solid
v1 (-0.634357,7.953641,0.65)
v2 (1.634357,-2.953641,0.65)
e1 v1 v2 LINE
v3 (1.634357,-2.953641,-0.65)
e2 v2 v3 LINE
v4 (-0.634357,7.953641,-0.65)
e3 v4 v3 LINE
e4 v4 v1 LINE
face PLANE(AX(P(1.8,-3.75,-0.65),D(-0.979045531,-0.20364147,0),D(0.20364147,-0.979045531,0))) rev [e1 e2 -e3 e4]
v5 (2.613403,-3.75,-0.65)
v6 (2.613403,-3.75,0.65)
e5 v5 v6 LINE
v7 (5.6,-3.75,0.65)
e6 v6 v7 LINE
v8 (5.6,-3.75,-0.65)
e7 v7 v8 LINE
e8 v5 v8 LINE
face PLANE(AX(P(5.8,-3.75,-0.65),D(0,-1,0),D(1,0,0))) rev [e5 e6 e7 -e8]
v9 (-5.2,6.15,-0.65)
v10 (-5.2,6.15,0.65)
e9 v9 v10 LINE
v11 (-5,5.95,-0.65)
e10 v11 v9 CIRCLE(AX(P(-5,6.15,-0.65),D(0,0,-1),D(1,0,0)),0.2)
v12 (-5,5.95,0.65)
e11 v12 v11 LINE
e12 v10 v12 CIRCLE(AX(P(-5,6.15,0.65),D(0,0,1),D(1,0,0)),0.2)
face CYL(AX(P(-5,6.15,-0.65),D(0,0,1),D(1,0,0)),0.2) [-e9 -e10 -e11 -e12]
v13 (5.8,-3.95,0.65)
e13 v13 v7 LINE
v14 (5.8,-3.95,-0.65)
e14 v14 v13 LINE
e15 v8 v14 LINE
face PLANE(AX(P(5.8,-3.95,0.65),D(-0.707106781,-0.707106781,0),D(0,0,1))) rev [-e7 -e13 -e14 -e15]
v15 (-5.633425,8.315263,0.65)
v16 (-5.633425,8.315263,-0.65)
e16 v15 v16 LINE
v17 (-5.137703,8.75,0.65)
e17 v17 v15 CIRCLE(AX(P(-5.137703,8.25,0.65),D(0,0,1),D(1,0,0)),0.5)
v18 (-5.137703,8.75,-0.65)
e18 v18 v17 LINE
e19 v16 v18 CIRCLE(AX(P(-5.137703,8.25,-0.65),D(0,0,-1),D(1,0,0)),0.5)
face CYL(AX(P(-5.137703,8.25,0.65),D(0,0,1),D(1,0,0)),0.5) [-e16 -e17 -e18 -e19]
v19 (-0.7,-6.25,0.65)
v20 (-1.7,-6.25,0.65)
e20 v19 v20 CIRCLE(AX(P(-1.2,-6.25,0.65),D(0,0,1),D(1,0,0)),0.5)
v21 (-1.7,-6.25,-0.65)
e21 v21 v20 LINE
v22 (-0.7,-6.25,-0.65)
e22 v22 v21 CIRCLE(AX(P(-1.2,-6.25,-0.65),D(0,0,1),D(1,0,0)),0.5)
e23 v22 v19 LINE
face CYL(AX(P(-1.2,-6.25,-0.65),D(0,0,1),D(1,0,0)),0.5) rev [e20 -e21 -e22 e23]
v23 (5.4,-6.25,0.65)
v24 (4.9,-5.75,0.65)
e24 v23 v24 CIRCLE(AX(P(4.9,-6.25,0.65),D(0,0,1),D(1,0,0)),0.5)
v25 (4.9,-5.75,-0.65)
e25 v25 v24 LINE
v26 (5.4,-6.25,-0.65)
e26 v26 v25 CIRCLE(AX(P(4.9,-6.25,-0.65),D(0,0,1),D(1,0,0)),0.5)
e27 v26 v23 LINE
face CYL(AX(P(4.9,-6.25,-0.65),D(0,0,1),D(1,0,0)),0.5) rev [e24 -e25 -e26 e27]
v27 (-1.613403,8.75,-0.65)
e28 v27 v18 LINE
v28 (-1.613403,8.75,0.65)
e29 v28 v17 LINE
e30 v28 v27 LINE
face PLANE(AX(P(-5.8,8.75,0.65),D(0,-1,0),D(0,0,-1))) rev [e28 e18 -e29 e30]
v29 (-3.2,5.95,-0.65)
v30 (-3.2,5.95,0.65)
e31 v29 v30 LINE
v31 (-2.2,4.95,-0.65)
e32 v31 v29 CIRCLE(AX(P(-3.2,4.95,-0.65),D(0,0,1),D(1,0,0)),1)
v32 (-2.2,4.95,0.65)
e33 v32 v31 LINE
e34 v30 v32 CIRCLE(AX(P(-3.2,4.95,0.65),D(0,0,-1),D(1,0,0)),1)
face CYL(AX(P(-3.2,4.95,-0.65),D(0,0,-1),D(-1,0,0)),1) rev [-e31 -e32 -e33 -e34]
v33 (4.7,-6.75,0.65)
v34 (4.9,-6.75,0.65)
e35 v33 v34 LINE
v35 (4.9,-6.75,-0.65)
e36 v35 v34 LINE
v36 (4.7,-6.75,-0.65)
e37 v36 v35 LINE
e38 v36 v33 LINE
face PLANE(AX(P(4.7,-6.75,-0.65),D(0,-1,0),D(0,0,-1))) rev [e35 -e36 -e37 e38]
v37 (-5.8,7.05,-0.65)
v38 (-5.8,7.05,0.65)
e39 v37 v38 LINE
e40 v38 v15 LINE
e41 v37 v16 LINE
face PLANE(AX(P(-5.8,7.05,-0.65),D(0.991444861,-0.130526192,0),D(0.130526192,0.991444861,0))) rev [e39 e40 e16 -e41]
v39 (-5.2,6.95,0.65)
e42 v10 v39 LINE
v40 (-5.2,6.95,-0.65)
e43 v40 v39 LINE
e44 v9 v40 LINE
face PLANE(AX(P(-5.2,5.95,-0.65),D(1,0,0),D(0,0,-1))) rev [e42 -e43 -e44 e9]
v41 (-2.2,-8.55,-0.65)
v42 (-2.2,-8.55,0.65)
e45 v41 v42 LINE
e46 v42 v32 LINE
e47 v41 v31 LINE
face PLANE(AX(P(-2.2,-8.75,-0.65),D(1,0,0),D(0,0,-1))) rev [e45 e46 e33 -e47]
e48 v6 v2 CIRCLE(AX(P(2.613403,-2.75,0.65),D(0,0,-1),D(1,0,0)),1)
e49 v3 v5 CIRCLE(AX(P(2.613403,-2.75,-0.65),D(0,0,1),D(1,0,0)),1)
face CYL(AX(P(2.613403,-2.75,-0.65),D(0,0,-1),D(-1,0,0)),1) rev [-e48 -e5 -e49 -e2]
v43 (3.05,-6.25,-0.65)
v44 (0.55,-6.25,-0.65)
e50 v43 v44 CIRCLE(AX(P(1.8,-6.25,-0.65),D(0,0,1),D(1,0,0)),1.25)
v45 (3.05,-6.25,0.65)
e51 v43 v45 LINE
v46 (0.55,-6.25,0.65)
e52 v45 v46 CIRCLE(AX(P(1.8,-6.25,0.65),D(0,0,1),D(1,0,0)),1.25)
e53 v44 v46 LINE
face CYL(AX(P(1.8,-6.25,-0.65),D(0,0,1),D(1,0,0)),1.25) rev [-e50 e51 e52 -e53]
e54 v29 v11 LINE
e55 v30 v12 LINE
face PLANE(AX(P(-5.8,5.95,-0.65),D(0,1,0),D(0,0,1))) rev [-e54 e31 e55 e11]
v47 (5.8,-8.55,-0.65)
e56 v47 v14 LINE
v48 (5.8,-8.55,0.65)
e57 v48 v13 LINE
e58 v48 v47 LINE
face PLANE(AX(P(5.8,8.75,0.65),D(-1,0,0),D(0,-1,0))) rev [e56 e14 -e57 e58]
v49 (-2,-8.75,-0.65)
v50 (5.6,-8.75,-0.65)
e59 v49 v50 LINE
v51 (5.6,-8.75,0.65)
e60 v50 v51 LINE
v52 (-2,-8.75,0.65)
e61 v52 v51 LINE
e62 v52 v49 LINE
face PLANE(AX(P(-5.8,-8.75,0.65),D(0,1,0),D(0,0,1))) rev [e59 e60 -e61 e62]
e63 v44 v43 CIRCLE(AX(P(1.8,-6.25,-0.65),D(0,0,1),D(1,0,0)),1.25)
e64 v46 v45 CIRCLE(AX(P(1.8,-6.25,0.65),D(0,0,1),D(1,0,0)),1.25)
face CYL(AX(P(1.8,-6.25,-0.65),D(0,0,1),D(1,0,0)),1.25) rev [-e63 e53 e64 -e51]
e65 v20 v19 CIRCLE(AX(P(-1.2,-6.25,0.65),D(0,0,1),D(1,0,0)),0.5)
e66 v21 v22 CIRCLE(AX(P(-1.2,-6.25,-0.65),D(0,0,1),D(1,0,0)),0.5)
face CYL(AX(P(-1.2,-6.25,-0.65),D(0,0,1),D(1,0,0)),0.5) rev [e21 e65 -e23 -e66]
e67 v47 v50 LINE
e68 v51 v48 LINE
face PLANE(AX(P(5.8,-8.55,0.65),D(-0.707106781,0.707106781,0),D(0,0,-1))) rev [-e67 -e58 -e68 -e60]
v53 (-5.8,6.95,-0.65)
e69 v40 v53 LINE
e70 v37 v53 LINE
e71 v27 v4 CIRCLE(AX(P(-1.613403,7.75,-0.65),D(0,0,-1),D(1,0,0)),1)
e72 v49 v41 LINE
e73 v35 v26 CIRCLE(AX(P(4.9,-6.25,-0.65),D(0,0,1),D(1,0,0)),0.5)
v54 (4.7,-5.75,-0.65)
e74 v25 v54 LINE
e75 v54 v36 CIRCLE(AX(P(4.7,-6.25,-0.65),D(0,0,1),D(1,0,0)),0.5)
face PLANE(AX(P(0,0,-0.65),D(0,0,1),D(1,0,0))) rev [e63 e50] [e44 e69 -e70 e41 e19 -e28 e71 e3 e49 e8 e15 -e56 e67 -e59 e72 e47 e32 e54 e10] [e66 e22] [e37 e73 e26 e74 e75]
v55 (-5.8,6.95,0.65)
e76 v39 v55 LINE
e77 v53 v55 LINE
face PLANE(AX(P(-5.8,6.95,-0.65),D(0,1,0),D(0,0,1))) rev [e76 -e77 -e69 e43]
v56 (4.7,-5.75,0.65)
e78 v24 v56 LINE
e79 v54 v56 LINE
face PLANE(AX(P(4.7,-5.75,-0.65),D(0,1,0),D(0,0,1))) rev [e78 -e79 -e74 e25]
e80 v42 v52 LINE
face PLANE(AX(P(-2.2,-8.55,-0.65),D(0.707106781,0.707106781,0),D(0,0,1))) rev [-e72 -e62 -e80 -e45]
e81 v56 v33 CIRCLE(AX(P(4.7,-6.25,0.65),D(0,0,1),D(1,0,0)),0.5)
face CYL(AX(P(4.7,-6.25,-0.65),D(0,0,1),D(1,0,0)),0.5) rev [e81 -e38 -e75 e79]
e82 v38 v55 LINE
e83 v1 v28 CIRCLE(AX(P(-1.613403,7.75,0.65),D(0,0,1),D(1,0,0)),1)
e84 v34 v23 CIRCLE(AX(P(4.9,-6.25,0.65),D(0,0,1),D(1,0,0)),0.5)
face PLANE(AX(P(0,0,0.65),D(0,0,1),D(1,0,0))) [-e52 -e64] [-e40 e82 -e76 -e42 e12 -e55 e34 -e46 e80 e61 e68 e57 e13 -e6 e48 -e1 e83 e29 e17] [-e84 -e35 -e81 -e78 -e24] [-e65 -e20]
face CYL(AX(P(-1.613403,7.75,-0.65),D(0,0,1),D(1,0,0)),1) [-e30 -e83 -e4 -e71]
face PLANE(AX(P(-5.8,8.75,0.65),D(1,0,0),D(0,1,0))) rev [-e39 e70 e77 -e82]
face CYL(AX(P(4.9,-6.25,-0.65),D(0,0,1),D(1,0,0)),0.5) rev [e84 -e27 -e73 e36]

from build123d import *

# Parameters (mm, degrees)
SKETCH1_W           = 11.6
SKETCH1_H           = 17.5
BOSS_EXTRUDE1_DEPTH = 0.65
SKETCH2_R           = 1.25
SKETCH2_R_2         = 0.5
CUT_EXTRUDE1_DEPTH  = 11.577925127
SKETCH3_W           = 3.6
SKETCH3_H           = 14.7
CUT_EXTRUDE2_DEPTH  = 11.577925127
SKETCH4_W           = 0.6
SKETCH4_H           = 1
CUT_EXTRUDE3_DEPTH  = 11.577925127
FILLET2_R           = 0.2
CUT_EXTRUDE4_DEPTH  = 11.577925127
FILLET3_R           = 1
CHAMFER1_SIZE       = 0.2
FILLET4_R           = 0.5


with BuildPart() as part:
    # Sketch1 → Boss-Extrude1 (new, symmetric)
    with BuildSketch(Plane.XY):
        Rectangle(SKETCH1_W, SKETCH1_H)
    extrude(amount=BOSS_EXTRUDE1_DEPTH, both=True)

    # Sketch2 → Cut-Extrude1 (cut, through all)
    with BuildSketch(Plane.XY.offset(0.65)):
        with Locations((1.8, -6.25)):
            Circle(SKETCH2_R)
        with Locations((-1.2, -6.25)):
            Circle(SKETCH2_R_2)
        with BuildLine():
            Line((4.7, -5.75), (4.9, -5.75))
            ThreePointArc((4.9, -5.75), (5.4, -6.25), (4.9, -6.75))
            Line((4.9, -6.75), (4.7, -6.75))
            ThreePointArc((4.7, -6.75), (4.2, -6.25), (4.7, -5.75))
        make_face()
    extrude(amount=-CUT_EXTRUDE1_DEPTH, mode=Mode.SUBTRACT)

    # Sketch3 → Cut-Extrude2 (cut, through all)
    with BuildSketch(Plane.XY.offset(0.65)):
        with Locations((-4, -1.4)):
            Rectangle(SKETCH3_W, SKETCH3_H)
        Polygon((5.8, -3.75), (1.8, -3.75), (-0.8, 8.75), (5.8, 8.75), align=None)
    extrude(amount=-CUT_EXTRUDE2_DEPTH, mode=Mode.SUBTRACT)

    # Sketch4 → Cut-Extrude3 (cut, through all)
    with BuildSketch(Plane.XY.offset(0.65)):
        with Locations((-5.5, 6.45)):
            Rectangle(SKETCH4_W, SKETCH4_H)
    extrude(amount=-CUT_EXTRUDE3_DEPTH, mode=Mode.SUBTRACT)

    # Fillet2
    fillet2_edges = [part.edges().sort_by_distance(p)[0] for p in [
        (-5.2, 5.95, 0),
    ]]
    fillet(fillet2_edges, radius=FILLET2_R)

    # Sketch5 → Cut-Extrude4 (cut, through all)
    with BuildSketch(Plane.XY.offset(0.65)):
        Polygon((-5.8, 7.05), (-5.576190754, 8.75), (-5.8, 8.75), align=None)
    extrude(amount=-CUT_EXTRUDE4_DEPTH, mode=Mode.SUBTRACT)

    # Fillet3
    fillet3_edges = [part.edges().sort_by_distance(p)[0] for p in [
        (-2.2, 5.95, 0),
        (1.8, -3.75, 0),
        (-0.8, 8.75, 0),
    ]]
    fillet(fillet3_edges, radius=FILLET3_R)

    # Chamfer1
    chamfer1_edges = [part.edges().sort_by_distance(p)[0] for p in [
        (-2.2, -8.75, 0),
        (5.8, -3.75, 0),
        (5.8, -8.75, 0),
    ]]
    chamfer(chamfer1_edges, length=CHAMFER1_SIZE)

    # Fillet4
    fillet4_edges = [part.edges().sort_by_distance(p)[0] for p in [
        (-5.576190754, 8.75, 0),
    ]]
    fillet(fillet4_edges, radius=FILLET4_R)


solid = part.part
